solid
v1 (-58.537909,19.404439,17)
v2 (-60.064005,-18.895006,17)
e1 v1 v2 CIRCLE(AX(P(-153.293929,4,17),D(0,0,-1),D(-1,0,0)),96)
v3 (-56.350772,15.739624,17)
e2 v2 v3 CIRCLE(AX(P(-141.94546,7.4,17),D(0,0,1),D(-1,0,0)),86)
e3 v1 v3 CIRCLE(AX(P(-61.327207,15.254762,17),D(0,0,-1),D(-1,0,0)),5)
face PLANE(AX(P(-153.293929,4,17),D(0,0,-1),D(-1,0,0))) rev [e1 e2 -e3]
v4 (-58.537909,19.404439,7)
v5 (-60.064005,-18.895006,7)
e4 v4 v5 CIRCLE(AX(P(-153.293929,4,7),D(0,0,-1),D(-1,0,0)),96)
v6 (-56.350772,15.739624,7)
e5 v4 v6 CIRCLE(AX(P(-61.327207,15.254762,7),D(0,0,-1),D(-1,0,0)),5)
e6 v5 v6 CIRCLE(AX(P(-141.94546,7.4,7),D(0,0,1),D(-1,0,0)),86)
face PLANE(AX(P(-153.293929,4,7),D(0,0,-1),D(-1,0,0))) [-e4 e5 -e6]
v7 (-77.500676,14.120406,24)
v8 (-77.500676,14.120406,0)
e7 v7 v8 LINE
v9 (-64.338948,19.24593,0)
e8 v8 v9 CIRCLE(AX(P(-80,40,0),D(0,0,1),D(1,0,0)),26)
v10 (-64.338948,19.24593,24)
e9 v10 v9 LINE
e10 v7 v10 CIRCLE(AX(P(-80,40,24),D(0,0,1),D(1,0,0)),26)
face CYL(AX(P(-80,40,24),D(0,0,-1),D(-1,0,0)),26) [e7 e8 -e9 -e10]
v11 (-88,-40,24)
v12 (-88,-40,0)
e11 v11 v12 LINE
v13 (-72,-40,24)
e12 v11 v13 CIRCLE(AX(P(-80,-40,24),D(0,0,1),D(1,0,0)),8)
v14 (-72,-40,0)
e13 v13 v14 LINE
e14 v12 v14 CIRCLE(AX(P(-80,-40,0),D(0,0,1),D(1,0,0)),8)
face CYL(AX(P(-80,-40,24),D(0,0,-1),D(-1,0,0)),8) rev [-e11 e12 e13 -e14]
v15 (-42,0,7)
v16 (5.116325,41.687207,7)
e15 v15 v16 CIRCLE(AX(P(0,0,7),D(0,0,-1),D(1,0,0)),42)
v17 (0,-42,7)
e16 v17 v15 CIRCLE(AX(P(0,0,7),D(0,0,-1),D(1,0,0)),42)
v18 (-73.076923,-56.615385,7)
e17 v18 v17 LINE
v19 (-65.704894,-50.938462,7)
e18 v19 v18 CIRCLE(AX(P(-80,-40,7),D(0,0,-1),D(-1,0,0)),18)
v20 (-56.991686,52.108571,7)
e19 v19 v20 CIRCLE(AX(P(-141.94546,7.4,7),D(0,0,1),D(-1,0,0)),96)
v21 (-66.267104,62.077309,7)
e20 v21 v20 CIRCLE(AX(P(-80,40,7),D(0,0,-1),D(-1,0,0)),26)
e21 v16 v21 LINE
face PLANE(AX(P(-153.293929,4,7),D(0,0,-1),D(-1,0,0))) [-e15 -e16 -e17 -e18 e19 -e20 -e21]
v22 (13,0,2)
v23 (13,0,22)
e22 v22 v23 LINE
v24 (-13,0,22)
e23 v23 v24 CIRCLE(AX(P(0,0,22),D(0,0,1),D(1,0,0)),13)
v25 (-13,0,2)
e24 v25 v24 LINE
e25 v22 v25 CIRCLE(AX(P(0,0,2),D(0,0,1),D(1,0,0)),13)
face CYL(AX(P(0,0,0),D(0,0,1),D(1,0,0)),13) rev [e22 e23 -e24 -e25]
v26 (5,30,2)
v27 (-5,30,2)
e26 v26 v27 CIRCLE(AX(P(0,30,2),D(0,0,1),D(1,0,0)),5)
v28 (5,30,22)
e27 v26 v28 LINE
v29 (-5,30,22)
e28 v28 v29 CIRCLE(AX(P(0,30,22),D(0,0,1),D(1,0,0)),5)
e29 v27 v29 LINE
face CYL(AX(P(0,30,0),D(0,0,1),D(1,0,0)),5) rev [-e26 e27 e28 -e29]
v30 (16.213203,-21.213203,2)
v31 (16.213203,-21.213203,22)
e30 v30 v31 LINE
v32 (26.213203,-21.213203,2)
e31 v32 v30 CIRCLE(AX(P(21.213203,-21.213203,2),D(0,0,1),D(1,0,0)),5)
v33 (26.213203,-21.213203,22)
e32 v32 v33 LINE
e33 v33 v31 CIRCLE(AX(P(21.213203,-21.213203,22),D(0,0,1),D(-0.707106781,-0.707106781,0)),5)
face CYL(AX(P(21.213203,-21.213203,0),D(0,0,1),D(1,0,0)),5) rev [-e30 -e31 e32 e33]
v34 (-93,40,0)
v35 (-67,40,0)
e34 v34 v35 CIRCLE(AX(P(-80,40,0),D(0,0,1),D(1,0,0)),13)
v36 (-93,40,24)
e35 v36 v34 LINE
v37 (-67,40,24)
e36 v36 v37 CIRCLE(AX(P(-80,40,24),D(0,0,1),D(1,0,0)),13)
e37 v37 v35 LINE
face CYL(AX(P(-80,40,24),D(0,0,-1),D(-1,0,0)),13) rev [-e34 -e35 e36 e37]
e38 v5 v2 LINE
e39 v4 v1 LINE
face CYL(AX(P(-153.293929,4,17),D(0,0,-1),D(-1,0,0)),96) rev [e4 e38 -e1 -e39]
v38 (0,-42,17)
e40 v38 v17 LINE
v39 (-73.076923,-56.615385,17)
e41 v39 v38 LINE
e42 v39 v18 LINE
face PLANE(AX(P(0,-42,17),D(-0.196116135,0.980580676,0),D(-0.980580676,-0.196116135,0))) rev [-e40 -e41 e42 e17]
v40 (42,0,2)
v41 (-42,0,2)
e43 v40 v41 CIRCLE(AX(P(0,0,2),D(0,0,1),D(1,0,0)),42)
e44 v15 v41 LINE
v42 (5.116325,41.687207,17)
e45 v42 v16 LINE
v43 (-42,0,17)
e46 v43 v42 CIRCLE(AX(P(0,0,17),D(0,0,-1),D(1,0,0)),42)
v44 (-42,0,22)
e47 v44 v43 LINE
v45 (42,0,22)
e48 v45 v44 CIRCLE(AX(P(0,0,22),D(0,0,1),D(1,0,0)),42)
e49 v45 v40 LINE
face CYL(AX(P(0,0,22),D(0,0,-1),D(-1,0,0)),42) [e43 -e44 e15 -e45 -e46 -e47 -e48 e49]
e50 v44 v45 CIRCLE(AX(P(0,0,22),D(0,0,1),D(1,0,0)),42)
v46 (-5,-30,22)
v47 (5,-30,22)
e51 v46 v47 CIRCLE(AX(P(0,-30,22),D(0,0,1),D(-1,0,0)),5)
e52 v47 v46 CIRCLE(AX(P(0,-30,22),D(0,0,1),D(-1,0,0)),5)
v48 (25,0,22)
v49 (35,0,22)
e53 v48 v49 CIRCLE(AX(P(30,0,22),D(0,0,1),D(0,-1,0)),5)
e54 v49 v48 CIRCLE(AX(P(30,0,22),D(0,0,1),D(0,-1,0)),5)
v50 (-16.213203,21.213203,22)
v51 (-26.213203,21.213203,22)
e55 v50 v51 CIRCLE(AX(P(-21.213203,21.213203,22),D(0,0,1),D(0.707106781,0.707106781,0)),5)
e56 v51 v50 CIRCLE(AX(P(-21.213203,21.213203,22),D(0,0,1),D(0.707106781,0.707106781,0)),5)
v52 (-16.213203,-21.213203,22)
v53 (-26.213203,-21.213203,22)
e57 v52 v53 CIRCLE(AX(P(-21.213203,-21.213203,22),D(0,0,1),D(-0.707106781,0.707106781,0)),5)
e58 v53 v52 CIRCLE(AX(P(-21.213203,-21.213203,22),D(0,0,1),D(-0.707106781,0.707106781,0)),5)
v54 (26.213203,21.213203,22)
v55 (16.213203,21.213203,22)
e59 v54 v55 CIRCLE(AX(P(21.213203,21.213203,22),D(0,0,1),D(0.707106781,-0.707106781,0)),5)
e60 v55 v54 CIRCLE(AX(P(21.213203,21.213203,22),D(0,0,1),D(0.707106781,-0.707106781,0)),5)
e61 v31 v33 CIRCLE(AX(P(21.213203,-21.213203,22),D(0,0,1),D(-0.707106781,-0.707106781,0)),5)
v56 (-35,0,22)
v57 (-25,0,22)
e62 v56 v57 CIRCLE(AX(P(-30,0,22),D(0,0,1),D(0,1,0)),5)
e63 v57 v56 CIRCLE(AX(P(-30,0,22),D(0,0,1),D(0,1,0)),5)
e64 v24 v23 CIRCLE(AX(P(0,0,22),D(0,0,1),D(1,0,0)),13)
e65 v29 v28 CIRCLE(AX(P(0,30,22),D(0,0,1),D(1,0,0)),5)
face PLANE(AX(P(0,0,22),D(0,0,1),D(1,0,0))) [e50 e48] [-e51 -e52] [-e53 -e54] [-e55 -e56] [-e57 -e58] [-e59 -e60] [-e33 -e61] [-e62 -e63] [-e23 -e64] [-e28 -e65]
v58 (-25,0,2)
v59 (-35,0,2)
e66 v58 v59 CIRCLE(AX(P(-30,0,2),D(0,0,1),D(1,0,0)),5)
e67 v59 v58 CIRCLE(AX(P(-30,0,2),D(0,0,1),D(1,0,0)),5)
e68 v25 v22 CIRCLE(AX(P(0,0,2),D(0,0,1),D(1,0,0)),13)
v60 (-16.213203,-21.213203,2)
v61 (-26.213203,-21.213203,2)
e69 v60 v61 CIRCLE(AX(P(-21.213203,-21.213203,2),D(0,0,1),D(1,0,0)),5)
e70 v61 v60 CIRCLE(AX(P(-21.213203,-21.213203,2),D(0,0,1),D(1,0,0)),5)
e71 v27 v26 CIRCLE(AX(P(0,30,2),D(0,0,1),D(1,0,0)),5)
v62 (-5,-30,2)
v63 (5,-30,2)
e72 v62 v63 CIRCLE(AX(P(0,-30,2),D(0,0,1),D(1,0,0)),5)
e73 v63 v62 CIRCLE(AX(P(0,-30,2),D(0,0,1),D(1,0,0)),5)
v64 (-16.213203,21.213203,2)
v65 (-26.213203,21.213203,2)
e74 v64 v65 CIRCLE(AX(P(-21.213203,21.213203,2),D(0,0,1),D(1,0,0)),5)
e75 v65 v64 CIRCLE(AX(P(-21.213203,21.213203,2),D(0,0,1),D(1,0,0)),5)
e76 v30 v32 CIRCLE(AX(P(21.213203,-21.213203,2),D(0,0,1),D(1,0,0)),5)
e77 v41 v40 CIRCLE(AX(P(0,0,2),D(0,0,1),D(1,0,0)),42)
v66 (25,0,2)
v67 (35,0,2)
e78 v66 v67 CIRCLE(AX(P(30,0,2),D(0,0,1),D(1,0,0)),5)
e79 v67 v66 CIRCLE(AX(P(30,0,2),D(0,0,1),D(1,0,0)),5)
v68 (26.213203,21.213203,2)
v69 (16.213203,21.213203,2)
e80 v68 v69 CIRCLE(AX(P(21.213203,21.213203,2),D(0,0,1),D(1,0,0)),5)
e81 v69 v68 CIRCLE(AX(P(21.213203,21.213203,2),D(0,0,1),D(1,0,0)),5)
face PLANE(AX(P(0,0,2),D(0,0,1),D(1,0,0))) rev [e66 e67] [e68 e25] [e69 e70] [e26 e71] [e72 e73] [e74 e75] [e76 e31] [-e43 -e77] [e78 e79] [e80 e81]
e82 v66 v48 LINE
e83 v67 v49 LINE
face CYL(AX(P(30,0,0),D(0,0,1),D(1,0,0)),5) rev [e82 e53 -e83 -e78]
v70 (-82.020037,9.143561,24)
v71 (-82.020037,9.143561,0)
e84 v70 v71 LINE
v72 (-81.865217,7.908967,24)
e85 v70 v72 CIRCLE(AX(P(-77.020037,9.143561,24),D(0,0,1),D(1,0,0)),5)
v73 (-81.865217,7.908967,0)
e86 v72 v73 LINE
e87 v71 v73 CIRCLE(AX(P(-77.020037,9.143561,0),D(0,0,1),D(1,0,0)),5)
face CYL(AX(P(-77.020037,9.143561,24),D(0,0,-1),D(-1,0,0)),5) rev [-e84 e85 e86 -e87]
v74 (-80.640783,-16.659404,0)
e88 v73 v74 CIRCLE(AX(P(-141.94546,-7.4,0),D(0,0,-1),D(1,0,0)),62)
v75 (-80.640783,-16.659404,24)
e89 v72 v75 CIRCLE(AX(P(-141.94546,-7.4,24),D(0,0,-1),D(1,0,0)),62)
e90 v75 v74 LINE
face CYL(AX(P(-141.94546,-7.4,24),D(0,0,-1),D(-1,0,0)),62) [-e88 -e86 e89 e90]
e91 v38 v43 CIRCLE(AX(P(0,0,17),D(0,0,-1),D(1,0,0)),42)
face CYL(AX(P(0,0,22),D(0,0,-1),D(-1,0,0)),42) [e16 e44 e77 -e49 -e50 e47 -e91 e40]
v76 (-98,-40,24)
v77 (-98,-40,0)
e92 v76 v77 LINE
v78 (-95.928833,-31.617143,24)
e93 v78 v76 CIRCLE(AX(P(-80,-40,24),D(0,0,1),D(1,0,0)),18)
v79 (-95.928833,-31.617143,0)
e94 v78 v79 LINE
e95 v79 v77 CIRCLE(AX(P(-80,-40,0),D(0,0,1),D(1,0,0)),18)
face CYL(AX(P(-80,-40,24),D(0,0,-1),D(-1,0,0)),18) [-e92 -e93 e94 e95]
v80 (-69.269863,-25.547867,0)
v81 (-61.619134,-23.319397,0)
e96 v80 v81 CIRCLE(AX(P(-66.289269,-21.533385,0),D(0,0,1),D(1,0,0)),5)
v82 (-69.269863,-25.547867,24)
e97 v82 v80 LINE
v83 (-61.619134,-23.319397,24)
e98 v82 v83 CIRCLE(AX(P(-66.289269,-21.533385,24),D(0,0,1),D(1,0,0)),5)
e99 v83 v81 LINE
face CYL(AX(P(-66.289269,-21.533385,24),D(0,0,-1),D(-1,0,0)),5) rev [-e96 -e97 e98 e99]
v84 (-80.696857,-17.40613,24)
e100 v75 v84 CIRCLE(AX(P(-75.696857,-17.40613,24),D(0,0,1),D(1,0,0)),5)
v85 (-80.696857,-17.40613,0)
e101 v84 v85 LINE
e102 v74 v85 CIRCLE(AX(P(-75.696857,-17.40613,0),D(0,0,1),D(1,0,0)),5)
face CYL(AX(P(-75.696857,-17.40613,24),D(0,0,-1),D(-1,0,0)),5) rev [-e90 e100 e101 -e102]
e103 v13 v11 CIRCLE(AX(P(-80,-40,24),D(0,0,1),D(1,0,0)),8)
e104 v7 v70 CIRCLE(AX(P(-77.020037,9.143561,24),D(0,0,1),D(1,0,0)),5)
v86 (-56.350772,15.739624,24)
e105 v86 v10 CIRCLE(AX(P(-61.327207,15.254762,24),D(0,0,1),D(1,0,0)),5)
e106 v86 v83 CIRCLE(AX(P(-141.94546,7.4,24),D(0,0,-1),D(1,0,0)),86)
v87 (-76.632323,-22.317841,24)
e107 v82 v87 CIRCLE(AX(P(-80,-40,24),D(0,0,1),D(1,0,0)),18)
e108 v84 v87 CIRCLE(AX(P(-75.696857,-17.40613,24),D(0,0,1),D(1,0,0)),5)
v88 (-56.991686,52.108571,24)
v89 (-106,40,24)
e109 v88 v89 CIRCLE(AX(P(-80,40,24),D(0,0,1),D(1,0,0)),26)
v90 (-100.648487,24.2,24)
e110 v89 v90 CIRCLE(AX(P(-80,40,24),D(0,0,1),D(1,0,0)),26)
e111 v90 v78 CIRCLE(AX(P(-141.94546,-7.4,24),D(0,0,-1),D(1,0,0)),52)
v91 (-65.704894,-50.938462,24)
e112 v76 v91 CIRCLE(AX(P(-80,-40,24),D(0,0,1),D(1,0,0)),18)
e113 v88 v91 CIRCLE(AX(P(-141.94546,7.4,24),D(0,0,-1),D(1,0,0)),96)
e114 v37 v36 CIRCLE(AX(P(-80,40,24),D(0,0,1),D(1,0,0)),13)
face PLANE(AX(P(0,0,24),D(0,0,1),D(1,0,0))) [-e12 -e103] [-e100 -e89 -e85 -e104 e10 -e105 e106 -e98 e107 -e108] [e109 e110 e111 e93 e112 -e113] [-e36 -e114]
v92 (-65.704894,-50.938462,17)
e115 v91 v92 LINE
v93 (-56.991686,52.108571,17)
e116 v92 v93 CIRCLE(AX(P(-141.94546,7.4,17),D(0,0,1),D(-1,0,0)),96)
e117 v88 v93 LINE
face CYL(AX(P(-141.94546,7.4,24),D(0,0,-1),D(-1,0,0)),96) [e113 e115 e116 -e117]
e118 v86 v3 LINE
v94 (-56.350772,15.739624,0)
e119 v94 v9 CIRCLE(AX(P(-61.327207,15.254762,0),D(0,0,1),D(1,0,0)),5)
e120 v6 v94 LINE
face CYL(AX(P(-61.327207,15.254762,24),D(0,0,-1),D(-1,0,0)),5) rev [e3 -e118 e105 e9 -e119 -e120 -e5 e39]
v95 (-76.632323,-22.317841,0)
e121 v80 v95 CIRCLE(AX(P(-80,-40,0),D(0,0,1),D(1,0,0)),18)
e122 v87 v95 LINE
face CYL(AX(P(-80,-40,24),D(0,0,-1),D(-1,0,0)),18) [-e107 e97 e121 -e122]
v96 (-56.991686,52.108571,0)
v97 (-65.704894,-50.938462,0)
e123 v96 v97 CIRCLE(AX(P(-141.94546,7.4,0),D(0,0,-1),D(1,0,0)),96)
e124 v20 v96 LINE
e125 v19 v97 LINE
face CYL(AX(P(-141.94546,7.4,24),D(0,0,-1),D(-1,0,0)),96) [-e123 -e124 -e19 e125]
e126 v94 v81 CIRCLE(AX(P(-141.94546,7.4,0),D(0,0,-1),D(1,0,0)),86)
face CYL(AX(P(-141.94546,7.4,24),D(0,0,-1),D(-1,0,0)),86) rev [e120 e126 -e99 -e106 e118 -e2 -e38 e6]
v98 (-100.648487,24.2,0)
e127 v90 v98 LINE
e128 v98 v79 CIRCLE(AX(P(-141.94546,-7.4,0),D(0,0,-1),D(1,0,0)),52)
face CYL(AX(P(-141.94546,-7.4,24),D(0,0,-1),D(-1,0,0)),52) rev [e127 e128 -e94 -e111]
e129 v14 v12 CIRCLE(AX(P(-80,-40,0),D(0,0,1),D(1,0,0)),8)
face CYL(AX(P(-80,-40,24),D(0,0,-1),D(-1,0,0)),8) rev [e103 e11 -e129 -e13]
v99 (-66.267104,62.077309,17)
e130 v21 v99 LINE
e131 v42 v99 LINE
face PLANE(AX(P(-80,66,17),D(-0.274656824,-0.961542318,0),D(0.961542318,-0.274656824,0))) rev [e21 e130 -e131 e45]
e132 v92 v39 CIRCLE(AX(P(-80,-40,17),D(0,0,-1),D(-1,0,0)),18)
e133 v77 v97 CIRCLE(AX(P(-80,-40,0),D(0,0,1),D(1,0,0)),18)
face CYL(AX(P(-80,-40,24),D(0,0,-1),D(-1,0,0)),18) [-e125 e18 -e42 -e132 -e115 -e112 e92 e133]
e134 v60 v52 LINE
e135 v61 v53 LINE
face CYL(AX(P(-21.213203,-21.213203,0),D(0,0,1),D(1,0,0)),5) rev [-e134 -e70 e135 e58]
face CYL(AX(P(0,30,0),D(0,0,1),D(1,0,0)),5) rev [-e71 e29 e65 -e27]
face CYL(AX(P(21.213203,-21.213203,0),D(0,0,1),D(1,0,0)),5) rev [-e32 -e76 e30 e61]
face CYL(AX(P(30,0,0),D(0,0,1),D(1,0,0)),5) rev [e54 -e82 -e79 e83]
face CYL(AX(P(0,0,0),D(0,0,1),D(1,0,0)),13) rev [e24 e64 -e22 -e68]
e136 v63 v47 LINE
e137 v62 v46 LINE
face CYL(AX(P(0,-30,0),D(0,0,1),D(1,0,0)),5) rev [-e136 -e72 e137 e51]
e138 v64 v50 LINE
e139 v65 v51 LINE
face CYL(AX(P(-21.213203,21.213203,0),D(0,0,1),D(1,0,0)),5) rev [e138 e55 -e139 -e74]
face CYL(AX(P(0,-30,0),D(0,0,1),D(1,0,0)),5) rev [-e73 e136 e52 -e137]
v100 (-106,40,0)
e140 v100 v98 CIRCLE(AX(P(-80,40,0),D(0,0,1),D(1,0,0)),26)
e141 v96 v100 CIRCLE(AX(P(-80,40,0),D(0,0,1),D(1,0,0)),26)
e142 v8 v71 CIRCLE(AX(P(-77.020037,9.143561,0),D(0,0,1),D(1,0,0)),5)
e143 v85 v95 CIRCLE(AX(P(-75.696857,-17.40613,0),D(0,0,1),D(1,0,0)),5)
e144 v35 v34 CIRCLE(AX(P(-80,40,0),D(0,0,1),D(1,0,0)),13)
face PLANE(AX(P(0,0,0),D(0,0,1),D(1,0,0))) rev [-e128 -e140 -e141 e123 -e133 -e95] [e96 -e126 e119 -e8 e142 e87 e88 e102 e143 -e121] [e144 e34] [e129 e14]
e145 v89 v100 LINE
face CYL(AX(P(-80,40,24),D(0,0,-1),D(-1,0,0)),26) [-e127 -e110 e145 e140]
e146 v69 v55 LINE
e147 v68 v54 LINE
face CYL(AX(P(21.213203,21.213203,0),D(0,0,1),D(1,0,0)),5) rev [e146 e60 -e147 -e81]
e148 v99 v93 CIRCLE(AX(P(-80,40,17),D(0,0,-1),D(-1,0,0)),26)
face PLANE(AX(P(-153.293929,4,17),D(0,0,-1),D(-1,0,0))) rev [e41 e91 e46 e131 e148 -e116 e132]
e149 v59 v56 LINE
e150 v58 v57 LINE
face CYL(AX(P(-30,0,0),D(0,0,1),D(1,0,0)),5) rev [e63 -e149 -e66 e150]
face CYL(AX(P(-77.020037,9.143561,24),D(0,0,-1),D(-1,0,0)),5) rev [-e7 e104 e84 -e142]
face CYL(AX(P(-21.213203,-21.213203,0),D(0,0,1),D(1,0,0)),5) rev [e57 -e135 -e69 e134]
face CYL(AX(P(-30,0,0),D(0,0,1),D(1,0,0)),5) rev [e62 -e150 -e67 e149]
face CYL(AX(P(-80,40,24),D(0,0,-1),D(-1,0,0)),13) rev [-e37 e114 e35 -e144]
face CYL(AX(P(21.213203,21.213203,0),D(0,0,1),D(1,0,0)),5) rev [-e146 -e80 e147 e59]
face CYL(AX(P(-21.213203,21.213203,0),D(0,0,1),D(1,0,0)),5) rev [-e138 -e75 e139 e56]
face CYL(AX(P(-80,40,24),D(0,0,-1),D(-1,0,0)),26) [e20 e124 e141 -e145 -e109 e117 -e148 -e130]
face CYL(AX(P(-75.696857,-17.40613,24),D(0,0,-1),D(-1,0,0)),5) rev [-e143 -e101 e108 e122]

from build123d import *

# Parameters (mm, degrees)
LINK_PLATE_PROFILE_R      = 8
LINK_PLATE_PROFILE_R_2    = 13
LINK_PLATE_DEPTH          = 24
HUB_DISC_PROFILE_84_R     = 42
HUB_DISC_84_DEPTH         = 10
HUB_RIB_DEPTH             = 5
HUB_CENTRE_BORE_SKETCH_R  = 13
HUB_CENTRE_BORE_DEPTH     = 127.791166885
HUB_HOLE_SKETCH_R         = 5
HUB_HOLE_DEPTH            = 127.791166885
HUB_HOLE_PATTERN_8X_COUNT = 8


with BuildPart() as part:
    # Link Plate Profile → Link Plate (new body)
    with BuildSketch(Plane.XY):
        with BuildLine():
            ThreePointArc((-65.704893873, -50.938461538), (-46.286814024, -0.688477763), (-56.99168633, 52.108571429))
            ThreePointArc((-56.99168633, 52.108571429), (-94.004081038, 61.906293942), (-100.648486627, 24.2))
            ThreePointArc((-100.648486627, 24.2), (-90.130360042, -3.018741212), (-95.928832541, -31.617142857))
            ThreePointArc((-95.928832541, -31.617142857), (-89.695133026, -55.165895806), (-65.704893873, -50.938461538))
        make_face()
        with Locations((-80, -40)):
            Circle(LINK_PLATE_PROFILE_R, mode=Mode.SUBTRACT)
        with BuildLine():
            ThreePointArc((-81.86521747, 7.908967037), (-81.11107364, 12.018176986), (-77.500675884, 14.120406128))
            ThreePointArc((-77.500675884, 14.120406128), (-70.565087966, 15.772279618), (-64.338947731, 19.245929512))
            ThreePointArc((-64.338947731, 19.245929512), (-59.317592319, 19.833129635), (-56.350771542, 15.739623969))
            ThreePointArc((-56.350771542, 15.739623969), (-56.717251337, -4.095758702), (-61.619133807, -23.319396791))
            ThreePointArc((-61.619133807, -23.319396791), (-64.890999648, -26.333889771), (-69.26986273, -25.547866796))
            ThreePointArc((-69.26986273, -25.547866796), (-72.768447006, -23.516534306), (-76.632322996, -22.317840867))
            ThreePointArc((-76.632322996, -22.317840867), (-79.776843452, -20.296408854), (-80.640782737, -16.659403878))
            ThreePointArc((-80.640782737, -16.659403878), (-80.022314885, -4.313883718), (-81.86521747, 7.908967037))
        make_face(mode=Mode.SUBTRACT)
        with Locations((-80, 40)):
            Circle(LINK_PLATE_PROFILE_R_2, mode=Mode.SUBTRACT)
    extrude(amount=LINK_PLATE_DEPTH)



with BuildPart() as body_2:
    # Hub Disc Profile Ø84 → Hub Disc Ø84 (new, symmetric)
    with BuildSketch(Plane.XY.offset(12)):
        Circle(HUB_DISC_PROFILE_84_R)
    extrude(amount=HUB_DISC_84_DEPTH, both=True)


with BuildPart() as part_1:
    add(part.part)

    add(body_2.part)  # Hub Rib merges body 2
    # Rib Profile → Hub Rib (add, symmetric)
    with BuildSketch(Plane.XY.offset(12)):
        with BuildLine():
            Line((-80, 66), (5.116324571, 41.687206945))
            ThreePointArc((5.116324571, 41.687206945), (-41.921728803, 2.562938577), (0, -42))
            Line((0, -42), (-80, -58))
            ThreePointArc((-80, -58), (-57.293928807, 4), (-80, 66))
        make_face()
    extrude(amount=HUB_RIB_DEPTH, both=True)

    # Hub Centre Bore Sketch → Hub Centre Bore (cut, through all)
    with BuildSketch(Plane.XY.offset(22)):
        Circle(HUB_CENTRE_BORE_SKETCH_R)
    extrude(amount=-HUB_CENTRE_BORE_DEPTH, mode=Mode.SUBTRACT)

    # Hub Hole Sketch → Hub Hole (cut, through all)
    with BuildSketch(Plane.XY.offset(22)):
        with Locations((0, 30)):
            Circle(HUB_HOLE_SKETCH_R)
    hub_hole = extrude(amount=-HUB_HOLE_DEPTH, mode=Mode.SUBTRACT)

    # Hub Hole Pattern 8x: Hub Hole ×8 about axis
    hub_hole_pattern_8x_axis = Axis((0, 0, 0), (0, 0, 1))
    for i in range(1, HUB_HOLE_PATTERN_8X_COUNT):
        add(hub_hole.rotate(hub_hole_pattern_8x_axis, i * 360 / HUB_HOLE_PATTERN_8X_COUNT), mode=Mode.SUBTRACT)


solid = part_1.part
